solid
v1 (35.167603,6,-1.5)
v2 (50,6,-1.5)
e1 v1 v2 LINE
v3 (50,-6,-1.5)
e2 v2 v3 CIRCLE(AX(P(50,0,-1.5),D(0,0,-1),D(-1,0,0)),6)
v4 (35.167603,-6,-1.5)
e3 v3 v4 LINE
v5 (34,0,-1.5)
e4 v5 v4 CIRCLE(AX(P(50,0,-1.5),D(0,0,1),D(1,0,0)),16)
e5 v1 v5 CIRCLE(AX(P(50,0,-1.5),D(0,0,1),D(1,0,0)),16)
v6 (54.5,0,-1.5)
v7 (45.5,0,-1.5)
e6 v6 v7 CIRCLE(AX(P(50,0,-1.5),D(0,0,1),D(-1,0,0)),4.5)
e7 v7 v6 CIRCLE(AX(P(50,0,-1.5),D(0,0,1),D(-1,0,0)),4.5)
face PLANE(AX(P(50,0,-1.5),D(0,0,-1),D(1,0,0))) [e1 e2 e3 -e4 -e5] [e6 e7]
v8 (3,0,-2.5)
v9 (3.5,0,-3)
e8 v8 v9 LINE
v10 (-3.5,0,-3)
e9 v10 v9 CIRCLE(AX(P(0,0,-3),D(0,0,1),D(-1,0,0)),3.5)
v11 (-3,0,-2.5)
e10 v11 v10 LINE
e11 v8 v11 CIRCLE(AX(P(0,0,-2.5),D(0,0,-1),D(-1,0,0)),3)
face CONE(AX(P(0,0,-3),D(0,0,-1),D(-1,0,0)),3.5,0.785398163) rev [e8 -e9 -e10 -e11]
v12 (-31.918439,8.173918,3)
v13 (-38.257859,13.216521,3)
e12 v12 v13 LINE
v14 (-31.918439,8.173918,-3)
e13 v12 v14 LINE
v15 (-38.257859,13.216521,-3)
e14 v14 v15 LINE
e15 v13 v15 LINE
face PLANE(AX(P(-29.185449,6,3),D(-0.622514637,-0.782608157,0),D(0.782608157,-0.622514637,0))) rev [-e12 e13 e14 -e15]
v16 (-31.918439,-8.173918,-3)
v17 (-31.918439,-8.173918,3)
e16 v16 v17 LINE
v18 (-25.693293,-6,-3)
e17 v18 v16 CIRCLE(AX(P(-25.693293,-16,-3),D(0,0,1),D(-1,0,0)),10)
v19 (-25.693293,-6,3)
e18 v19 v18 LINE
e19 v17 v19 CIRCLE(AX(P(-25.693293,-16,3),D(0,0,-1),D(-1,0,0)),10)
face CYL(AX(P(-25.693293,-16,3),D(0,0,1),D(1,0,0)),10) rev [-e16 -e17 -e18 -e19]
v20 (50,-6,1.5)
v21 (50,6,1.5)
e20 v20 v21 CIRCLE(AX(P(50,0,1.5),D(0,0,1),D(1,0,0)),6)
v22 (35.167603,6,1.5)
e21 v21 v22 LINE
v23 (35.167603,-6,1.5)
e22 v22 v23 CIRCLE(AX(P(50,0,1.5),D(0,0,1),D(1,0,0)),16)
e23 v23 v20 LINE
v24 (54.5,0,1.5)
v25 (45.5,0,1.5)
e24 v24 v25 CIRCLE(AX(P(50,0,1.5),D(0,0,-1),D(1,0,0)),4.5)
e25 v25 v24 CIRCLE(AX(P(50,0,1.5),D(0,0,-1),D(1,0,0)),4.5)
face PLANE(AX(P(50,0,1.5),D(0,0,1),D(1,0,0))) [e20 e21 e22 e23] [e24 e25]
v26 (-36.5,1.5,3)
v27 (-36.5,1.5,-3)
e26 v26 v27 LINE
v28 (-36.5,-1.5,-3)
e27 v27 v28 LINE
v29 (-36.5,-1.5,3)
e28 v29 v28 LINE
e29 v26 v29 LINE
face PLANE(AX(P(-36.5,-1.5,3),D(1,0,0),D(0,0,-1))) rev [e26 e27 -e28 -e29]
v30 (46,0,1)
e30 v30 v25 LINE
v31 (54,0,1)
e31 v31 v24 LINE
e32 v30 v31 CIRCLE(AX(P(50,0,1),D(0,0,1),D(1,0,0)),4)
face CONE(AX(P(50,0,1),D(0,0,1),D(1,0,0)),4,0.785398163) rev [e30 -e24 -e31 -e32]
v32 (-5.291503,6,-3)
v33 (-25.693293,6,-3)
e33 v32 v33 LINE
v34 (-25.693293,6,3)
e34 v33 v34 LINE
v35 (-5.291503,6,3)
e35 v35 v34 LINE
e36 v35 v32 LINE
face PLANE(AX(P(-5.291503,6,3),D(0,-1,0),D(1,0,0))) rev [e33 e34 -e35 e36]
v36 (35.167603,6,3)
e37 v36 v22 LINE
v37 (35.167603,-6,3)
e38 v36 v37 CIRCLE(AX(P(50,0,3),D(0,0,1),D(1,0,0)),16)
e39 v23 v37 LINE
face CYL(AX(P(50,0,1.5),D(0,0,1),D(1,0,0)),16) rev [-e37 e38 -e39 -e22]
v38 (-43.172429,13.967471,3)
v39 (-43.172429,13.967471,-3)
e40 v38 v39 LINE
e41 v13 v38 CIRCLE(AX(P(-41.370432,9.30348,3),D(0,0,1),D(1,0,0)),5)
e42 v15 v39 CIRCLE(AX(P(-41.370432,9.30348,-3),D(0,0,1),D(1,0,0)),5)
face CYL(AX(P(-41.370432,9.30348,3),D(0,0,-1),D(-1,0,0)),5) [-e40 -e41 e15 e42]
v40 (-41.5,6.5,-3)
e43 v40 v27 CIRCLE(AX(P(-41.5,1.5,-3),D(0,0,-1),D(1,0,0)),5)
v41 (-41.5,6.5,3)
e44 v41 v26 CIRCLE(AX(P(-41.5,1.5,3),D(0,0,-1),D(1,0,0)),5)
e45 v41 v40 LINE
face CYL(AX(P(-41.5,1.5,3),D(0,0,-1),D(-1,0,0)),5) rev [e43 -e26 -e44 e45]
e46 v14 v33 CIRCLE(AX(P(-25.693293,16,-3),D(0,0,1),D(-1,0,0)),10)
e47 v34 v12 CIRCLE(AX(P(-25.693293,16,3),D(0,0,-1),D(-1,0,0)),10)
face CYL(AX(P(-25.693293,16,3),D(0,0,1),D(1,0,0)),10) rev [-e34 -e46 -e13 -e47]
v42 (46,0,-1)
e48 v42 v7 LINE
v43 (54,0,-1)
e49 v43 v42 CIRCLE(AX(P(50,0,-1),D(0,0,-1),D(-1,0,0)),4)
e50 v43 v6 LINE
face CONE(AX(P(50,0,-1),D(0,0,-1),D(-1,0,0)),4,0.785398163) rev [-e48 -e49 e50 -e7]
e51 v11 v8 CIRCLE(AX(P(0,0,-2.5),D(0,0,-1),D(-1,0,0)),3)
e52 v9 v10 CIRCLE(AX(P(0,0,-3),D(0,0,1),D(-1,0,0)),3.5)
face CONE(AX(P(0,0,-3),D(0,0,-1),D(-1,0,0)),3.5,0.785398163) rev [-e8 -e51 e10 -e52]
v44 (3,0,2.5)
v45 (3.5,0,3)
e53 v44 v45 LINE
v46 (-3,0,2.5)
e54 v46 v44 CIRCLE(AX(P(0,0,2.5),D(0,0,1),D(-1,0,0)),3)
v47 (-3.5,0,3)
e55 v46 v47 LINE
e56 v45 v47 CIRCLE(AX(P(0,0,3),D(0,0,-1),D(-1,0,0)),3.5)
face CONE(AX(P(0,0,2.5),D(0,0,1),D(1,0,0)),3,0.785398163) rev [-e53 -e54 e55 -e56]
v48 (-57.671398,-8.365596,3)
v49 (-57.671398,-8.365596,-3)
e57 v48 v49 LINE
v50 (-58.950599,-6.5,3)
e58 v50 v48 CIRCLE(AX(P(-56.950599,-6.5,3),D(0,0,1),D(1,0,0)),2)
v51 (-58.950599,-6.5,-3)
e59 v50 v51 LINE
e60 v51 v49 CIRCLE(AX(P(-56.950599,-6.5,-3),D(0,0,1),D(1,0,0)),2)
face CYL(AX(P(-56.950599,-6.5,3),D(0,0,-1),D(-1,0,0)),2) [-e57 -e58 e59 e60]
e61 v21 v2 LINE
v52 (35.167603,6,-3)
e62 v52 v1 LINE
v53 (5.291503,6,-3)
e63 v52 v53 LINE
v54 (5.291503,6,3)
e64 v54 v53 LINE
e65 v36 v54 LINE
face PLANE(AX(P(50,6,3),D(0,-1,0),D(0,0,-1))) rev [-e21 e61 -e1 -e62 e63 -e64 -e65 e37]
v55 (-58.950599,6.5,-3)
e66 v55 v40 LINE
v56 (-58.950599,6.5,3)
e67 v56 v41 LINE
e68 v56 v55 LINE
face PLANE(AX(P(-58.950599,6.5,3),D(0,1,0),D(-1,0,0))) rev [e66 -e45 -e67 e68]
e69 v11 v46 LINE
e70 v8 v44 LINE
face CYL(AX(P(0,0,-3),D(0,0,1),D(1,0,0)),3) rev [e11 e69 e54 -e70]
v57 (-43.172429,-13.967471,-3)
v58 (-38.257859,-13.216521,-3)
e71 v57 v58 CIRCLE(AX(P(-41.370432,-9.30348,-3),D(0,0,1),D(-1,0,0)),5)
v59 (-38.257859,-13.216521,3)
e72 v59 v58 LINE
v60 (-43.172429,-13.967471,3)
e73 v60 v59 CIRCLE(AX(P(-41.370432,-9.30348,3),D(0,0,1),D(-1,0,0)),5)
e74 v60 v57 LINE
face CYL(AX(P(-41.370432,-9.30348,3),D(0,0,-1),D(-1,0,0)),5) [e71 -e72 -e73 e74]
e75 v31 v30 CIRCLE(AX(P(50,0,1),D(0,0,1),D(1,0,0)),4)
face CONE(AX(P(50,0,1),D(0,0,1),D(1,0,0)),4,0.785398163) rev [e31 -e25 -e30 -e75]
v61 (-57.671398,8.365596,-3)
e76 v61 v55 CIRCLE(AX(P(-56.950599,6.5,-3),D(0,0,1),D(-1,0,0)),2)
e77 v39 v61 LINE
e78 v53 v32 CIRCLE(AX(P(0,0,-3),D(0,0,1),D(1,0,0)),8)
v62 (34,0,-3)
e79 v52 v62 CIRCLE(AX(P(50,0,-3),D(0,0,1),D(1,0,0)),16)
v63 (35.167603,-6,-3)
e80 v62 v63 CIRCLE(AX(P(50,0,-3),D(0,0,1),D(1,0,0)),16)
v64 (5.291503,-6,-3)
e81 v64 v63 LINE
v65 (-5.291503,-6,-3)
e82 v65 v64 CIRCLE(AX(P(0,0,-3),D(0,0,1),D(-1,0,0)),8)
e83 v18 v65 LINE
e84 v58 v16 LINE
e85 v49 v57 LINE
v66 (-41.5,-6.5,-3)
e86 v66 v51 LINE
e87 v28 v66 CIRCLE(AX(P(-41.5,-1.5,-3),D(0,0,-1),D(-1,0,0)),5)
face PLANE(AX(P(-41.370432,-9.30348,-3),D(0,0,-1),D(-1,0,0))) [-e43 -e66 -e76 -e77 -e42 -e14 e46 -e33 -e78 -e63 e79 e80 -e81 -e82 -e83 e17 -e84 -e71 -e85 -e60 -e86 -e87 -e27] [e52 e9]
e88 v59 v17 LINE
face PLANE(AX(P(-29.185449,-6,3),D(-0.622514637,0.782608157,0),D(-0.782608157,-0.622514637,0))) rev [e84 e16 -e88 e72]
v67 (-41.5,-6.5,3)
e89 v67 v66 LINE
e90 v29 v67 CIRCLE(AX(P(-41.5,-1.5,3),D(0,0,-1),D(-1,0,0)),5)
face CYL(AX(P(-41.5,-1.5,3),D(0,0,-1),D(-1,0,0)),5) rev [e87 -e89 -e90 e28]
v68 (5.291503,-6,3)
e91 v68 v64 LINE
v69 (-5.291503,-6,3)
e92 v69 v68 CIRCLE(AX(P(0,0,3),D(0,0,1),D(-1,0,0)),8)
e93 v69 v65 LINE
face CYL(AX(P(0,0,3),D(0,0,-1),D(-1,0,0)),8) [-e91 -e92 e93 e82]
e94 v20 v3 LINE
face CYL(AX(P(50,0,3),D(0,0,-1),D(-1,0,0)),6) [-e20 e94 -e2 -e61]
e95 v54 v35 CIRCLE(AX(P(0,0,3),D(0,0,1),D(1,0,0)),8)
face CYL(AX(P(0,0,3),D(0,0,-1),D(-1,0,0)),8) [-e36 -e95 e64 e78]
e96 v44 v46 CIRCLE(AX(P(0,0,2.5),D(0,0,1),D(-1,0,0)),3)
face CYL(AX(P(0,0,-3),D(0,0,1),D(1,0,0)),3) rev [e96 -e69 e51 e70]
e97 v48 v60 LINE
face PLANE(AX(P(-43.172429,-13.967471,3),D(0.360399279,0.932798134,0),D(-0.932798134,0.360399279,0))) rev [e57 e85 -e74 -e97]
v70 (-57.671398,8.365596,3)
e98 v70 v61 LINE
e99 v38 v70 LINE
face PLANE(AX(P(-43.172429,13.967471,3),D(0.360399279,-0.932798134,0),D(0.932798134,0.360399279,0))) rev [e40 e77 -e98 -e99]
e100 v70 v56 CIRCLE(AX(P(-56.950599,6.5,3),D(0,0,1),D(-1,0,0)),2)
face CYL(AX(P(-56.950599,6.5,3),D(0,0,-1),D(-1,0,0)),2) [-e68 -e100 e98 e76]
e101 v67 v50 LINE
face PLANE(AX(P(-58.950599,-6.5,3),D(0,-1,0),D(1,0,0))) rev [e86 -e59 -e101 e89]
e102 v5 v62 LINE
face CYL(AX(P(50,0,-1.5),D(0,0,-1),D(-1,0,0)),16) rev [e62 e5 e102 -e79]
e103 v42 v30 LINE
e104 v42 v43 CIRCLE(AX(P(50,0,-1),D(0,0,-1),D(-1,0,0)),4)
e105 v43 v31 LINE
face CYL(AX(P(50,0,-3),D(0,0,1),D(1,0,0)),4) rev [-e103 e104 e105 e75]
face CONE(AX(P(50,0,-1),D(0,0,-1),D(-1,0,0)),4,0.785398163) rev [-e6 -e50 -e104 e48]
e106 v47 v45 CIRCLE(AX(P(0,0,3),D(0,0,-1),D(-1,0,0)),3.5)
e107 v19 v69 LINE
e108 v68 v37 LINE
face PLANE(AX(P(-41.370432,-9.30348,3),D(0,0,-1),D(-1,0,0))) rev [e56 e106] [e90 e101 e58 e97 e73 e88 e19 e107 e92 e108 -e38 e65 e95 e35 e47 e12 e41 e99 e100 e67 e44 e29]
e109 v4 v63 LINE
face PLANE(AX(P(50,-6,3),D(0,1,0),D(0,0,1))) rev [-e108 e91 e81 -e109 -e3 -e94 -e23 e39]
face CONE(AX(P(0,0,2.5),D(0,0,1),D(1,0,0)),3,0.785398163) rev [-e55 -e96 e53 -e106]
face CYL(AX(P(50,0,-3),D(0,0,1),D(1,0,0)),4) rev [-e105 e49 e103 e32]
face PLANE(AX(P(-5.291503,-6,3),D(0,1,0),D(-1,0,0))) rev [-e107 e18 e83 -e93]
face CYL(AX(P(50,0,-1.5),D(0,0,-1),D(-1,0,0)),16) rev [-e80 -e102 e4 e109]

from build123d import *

# Parameters (mm, degrees)
BOSS_EXTRUDE1_DEPTH     = 3
SKETCH3_R               = 16
CUT_EXTRUDE1_DEPTH      = 1.5
CUT_EXTRUDE2_DEPTH      = 61.827729708
CUT_EXTRUDE2_DEPTH_BACK = 61.827729708
SKETCH4_R               = 4
SKETCH4_R_2             = 3
CHAMFER1_SIZE           = 0.5
FILLET1_R               = 10


with BuildPart() as part:
    # Sketch1 → Boss-Extrude1 (new, symmetric)
    with BuildSketch(Plane.XY):
        with BuildLine():
            Line((50, 6), (5.291502622, 6))
            ThreePointArc((5.291502622, 6), (0, 8), (-5.291502622, 6))
            Line((-5.291502622, 6), (-29.18544931, 6))
            Line((-29.18544931, 6), (-38.257859313, 13.216520767))
            ThreePointArc((-38.257859313, 13.216520767), (-40.615194579, 14.246112449), (-43.172428892, 13.967470655))
            Line((-43.172428892, 13.967470655), (-57.671397892, 8.365596269))
            ThreePointArc((-57.671397892, 8.365596269), (-58.600083665, 7.631017879), (-58.950599334, 6.5))
            Line((-58.950599334, 6.5), (-41.5, 6.5))
            ThreePointArc((-41.5, 6.5), (-37.964466094, 5.035533906), (-36.5, 1.5))
            Line((-36.5, 1.5), (-36.5, -1.5))
            ThreePointArc((-36.5, -1.5), (-37.964466094, -5.035533906), (-41.5, -6.5))
            Line((-41.5, -6.5), (-58.950599334, -6.5))
            ThreePointArc((-58.950599334, -6.5), (-58.600083665, -7.631017879), (-57.671397892, -8.365596269))
            Line((-57.671397892, -8.365596269), (-43.172428892, -13.967470655))
            ThreePointArc((-43.172428892, -13.967470655), (-40.615194579, -14.246112449), (-38.257859313, -13.216520767))
            Line((-38.257859313, -13.216520767), (-29.18544931, -6))
            Line((-29.18544931, -6), (-5.291502622, -6))
            ThreePointArc((-5.291502622, -6), (0, -8), (5.291502622, -6))
            Line((5.291502622, -6), (50, -6))
            ThreePointArc((50, -6), (56, 0), (50, 6))
        make_face()
    extrude(amount=BOSS_EXTRUDE1_DEPTH, both=True)

    # Sketch3 → Cut-Extrude1 (cut)
    with BuildSketch(Plane.XY.offset(3)):
        with Locations((50, 0)):
            Circle(SKETCH3_R)
    cut_extrude1 = extrude(amount=-CUT_EXTRUDE1_DEPTH, mode=Mode.SUBTRACT)

    # Mirror1: Cut-Extrude1 across plane
    add(cut_extrude1.mirror(Plane.XY), mode=Mode.SUBTRACT)

    # Sketch4 → Cut-Extrude2 (cut, two sides: drawn at the far end of the back side and taken through both)
    with BuildSketch(Plane.XY.offset(1.5).offset(-CUT_EXTRUDE2_DEPTH_BACK)):
        with Locations((50, 0)):
            Circle(SKETCH4_R)
        Circle(SKETCH4_R_2)
    extrude(amount=CUT_EXTRUDE2_DEPTH + CUT_EXTRUDE2_DEPTH_BACK, mode=Mode.SUBTRACT)

    # Chamfer1
    chamfer1_edges = [part.edges().sort_by_distance(p)[0] for p in [
        (46, 0, 1.5),
        (46, 0, -1.5),
        (-3, 0, -3),
        (-3, 0, 3),
    ]]
    chamfer(chamfer1_edges, length=CHAMFER1_SIZE)

    # Fillet1
    fillet1_edges = [part.edges().sort_by_distance(p)[0] for p in [
        (-29.18544931, 6, 0),
        (-29.18544931, -6, 0),
    ]]
    fillet(fillet1_edges, radius=FILLET1_R)


solid = part.part
